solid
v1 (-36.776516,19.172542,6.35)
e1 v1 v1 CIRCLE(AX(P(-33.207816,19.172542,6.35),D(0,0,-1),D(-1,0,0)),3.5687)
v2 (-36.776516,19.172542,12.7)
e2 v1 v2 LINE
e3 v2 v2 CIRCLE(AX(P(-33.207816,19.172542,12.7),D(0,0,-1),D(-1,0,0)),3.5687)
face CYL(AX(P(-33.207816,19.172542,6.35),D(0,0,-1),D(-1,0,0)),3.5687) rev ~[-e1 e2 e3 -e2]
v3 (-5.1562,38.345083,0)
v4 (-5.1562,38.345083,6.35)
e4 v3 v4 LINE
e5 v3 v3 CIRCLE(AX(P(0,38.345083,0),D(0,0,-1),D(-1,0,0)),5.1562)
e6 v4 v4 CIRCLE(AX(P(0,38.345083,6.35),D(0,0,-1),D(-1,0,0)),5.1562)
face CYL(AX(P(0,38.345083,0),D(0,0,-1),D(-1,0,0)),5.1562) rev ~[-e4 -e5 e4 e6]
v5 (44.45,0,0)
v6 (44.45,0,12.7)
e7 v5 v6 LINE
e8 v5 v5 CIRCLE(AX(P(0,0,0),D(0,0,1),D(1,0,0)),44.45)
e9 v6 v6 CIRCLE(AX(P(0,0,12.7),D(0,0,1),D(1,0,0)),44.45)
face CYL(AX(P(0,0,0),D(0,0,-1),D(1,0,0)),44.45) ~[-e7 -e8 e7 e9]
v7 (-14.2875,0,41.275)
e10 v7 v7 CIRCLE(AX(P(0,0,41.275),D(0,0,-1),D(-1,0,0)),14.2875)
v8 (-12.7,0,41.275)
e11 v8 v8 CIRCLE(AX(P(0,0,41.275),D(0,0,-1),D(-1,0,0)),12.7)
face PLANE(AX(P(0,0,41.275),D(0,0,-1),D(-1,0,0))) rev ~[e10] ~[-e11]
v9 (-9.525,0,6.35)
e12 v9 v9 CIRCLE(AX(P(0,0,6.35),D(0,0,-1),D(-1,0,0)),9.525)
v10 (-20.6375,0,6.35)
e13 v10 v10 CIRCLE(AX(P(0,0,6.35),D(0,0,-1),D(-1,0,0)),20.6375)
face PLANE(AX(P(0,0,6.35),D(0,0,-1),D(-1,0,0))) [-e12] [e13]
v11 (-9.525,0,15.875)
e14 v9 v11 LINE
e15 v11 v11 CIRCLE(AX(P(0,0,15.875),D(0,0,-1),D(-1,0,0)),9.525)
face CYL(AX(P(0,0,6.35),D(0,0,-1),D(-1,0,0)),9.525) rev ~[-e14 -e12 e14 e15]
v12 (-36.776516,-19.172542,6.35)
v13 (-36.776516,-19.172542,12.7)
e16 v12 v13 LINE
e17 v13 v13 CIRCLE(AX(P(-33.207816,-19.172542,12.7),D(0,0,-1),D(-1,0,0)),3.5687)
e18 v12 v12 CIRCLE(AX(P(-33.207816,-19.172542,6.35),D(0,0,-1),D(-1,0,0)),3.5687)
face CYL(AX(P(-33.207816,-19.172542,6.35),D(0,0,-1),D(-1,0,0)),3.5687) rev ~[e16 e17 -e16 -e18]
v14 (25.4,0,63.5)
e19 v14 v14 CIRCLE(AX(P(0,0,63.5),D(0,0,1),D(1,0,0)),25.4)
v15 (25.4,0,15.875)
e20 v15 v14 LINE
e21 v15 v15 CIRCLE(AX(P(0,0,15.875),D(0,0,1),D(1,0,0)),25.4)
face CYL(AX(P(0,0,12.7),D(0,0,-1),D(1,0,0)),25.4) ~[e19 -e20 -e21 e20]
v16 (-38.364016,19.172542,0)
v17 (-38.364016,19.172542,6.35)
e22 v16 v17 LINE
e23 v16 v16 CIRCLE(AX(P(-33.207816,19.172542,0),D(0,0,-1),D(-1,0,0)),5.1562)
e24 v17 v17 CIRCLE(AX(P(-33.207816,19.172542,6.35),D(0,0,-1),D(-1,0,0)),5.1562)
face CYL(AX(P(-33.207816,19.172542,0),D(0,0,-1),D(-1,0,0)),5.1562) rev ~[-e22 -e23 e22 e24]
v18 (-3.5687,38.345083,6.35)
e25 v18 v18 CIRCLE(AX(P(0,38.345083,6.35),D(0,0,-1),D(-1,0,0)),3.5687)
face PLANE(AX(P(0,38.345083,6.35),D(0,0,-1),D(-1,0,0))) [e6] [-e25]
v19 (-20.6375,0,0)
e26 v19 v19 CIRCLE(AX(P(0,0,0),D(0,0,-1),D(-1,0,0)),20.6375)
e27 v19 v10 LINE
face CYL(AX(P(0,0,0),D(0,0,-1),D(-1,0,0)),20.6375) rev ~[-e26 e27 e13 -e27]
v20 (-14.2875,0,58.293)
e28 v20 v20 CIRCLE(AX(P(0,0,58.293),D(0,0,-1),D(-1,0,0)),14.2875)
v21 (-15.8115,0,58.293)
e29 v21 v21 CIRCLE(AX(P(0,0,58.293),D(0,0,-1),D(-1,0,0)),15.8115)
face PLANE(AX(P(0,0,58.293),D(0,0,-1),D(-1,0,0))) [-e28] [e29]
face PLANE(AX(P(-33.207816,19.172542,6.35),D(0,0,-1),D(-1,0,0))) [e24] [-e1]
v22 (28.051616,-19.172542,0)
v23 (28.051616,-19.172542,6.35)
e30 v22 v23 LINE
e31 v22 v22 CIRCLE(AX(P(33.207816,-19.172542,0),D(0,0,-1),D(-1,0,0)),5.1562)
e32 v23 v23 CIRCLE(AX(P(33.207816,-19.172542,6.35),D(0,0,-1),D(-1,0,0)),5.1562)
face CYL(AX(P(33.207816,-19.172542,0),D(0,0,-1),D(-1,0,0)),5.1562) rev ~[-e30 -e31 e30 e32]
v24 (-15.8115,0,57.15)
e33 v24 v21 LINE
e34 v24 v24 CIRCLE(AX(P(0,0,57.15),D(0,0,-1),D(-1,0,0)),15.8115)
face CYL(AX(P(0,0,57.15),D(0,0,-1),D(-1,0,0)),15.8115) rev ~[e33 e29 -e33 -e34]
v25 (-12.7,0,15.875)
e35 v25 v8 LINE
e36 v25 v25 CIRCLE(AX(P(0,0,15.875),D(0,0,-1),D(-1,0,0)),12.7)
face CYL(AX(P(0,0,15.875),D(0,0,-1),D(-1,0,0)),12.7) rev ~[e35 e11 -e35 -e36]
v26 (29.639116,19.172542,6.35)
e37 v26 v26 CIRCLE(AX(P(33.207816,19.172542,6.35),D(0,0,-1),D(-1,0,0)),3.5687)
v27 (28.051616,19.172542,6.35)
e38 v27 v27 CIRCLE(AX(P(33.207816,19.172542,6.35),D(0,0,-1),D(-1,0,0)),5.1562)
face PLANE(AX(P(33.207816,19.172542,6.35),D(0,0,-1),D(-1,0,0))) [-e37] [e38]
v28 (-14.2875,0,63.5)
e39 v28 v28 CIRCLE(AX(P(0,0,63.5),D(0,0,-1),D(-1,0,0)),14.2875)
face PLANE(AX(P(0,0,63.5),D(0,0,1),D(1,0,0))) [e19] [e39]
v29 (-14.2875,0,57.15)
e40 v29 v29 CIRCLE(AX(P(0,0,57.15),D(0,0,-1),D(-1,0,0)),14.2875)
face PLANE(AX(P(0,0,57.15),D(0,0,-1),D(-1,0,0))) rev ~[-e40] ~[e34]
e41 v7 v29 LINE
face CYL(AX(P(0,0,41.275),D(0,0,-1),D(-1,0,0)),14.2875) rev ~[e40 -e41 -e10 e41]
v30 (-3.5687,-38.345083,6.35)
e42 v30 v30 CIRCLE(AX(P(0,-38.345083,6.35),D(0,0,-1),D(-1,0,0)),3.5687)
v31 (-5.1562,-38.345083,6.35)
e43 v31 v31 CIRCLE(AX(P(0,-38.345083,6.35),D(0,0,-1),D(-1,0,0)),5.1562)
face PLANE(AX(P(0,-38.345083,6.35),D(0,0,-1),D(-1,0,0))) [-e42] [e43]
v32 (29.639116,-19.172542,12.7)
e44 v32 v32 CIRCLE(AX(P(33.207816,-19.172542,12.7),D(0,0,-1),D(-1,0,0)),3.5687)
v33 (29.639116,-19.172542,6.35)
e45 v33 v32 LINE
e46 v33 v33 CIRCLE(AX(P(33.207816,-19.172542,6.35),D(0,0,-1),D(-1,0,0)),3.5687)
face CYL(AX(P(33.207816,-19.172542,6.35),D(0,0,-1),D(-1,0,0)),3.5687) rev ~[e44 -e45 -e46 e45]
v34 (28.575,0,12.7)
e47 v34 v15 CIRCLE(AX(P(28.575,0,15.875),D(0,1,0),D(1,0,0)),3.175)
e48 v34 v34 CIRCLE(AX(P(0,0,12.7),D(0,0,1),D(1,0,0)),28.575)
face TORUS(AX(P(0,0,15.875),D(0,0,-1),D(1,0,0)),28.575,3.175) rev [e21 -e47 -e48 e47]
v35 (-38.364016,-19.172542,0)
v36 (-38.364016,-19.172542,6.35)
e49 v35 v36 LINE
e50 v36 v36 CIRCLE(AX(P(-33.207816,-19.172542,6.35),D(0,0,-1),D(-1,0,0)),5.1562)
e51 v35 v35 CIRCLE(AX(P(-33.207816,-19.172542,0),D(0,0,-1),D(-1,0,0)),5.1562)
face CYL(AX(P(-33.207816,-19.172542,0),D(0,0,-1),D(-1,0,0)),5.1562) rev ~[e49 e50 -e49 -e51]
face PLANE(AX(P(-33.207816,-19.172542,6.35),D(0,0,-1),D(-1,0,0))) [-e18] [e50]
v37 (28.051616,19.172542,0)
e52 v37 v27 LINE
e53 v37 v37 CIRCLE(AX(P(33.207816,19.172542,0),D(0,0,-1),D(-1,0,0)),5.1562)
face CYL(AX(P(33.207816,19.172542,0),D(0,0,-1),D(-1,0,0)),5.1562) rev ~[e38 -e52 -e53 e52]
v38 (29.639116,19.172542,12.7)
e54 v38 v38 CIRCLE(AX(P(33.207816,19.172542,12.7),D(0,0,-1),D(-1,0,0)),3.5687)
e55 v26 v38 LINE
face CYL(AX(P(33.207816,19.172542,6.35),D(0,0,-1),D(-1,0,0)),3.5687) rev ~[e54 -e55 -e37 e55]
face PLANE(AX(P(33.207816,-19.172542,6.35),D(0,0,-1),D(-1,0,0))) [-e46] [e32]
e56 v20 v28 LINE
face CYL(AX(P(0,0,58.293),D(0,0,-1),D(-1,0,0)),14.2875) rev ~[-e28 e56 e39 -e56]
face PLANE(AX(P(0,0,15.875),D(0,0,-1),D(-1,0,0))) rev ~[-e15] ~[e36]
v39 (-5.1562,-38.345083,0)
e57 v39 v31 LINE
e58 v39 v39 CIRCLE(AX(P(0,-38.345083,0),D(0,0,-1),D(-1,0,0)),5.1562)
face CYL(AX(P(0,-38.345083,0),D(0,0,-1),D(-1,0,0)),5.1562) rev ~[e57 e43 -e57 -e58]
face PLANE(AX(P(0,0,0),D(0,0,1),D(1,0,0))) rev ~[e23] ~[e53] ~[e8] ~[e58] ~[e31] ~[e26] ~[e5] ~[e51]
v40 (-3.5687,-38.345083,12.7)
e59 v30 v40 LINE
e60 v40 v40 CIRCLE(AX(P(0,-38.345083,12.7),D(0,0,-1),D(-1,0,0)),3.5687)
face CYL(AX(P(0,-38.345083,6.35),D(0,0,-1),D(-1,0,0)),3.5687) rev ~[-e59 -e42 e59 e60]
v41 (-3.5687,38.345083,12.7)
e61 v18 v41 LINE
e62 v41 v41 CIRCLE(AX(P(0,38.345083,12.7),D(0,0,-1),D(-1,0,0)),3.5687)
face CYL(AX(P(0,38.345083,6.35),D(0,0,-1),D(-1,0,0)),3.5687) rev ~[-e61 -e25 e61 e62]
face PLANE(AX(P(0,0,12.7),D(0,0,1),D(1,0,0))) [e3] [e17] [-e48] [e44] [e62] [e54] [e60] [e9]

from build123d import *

# Parameters (mm, degrees)
FLANGE_SKETCH_R                   = 44.45
FLANGE_3_5_DEPTH                  = 12.7
HUB_BOSS_SKETCH_R                 = 25.4
HUB_BOSS_2_DEPTH                  = 50.8
REAR_RECESS_SKETCH_R              = 20.6375
REAR_RECESS_1_625_DEPTH           = 6.35
PILOT_BORE_SKETCH_R               = 9.525
PILOT_BORE_0_75_DEPTH             = 9.525
INNER_BORE_SKETCH_R               = 12.7
INNER_BORE_1_0_DEPTH              = 25.4
BEARING_BORE_SKETCH_R             = 14.2875
BEARING_BORE_1_125_DEPTH          = 15.875
RETAINING_GROOVE_SKETCH_R         = 15.8115
RETAINING_RING_GROOVE_1_245_DEPTH = 1.143
THROUGH_BORE_SKETCH_R             = 14.2875
THROUGH_BORE_1_125_DEPTH          = 86.730267986
BOLT_COUNTERBORE_SKETCH_R         = 5.1562
BOLT_COUNTERBORES_6X_0_406_DEPTH  = 6.35
BOLT_HOLE_SKETCH_R                = 3.5687
BOLT_HOLES_6X_0_281_DEPTH         = 85.957209818
HUB_ROOT_FILLET_R0_125_R          = 3.175


with BuildPart() as part:
    # Flange Sketch → Flange Ø3.5 (new body)
    with BuildSketch(Plane.XY):
        Circle(FLANGE_SKETCH_R)
    extrude(amount=FLANGE_3_5_DEPTH)

    # Hub Boss Sketch → Hub Boss Ø2 (add)
    with BuildSketch(Plane.XY.offset(12.7)):
        Circle(HUB_BOSS_SKETCH_R)
    extrude(amount=HUB_BOSS_2_DEPTH)

    # Rear Recess Sketch → Rear Recess Ø1.625 (cut)
    with BuildSketch(Plane(origin=(0, 0, 0), x_dir=(-1, 0, 0), z_dir=(0, 0, -1))):
        Circle(REAR_RECESS_SKETCH_R)
    extrude(amount=-REAR_RECESS_1_625_DEPTH, mode=Mode.SUBTRACT)

    # Pilot Bore Sketch → Pilot Bore Ø0.75 (cut)
    with BuildSketch(Plane(origin=(0, 0, 6.35), x_dir=(-1, 0, 0), z_dir=(0, 0, -1))):
        Circle(PILOT_BORE_SKETCH_R)
    extrude(amount=-PILOT_BORE_0_75_DEPTH, mode=Mode.SUBTRACT)

    # Inner Bore Sketch → Inner Bore Ø1.0 (cut)
    with BuildSketch(Plane(origin=(0, 0, 15.875), x_dir=(-1, 0, 0), z_dir=(0, 0, -1))):
        Circle(INNER_BORE_SKETCH_R)
    extrude(amount=-INNER_BORE_1_0_DEPTH, mode=Mode.SUBTRACT)

    # Bearing Bore Sketch → Bearing Bore Ø1.125 (cut)
    with BuildSketch(Plane(origin=(0, 0, 41.275), x_dir=(-1, 0, 0), z_dir=(0, 0, -1))):
        Circle(BEARING_BORE_SKETCH_R)
    extrude(amount=-BEARING_BORE_1_125_DEPTH, mode=Mode.SUBTRACT)

    # Retaining Groove Sketch → Retaining Ring Groove Ø1.245 (cut)
    with BuildSketch(Plane(origin=(0, 0, 57.15), x_dir=(-1, 0, 0), z_dir=(0, 0, -1))):
        Circle(RETAINING_GROOVE_SKETCH_R)
    extrude(amount=-RETAINING_RING_GROOVE_1_245_DEPTH, mode=Mode.SUBTRACT)

    # Through Bore Sketch → Through Bore Ø1.125 (cut, through all)
    with BuildSketch(Plane(origin=(0, 0, 58.293), x_dir=(-1, 0, 0), z_dir=(0, 0, -1))):
        Circle(THROUGH_BORE_SKETCH_R)
    extrude(amount=-THROUGH_BORE_1_125_DEPTH, mode=Mode.SUBTRACT)

    # Bolt Counterbore Sketch → Bolt Counterbores 6xØ0.406 (cut)
    with BuildSketch(Plane(origin=(0, 0, 0), x_dir=(-1, 0, 0), z_dir=(0, 0, -1))):
        with Locations((0, 38.345083234)):
            Circle(BOLT_COUNTERBORE_SKETCH_R)
        with Locations((33.207816191, 19.172541617)):
            Circle(BOLT_COUNTERBORE_SKETCH_R)
        with Locations((33.207816191, -19.172541617)):
            Circle(BOLT_COUNTERBORE_SKETCH_R)
        with Locations((0, -38.345083234)):
            Circle(BOLT_COUNTERBORE_SKETCH_R)
        with Locations((-33.207816191, -19.172541617)):
            Circle(BOLT_COUNTERBORE_SKETCH_R)
        with Locations((-33.207816191, 19.172541617)):
            Circle(BOLT_COUNTERBORE_SKETCH_R)
    extrude(amount=-BOLT_COUNTERBORES_6X_0_406_DEPTH, mode=Mode.SUBTRACT)

    # Bolt Hole Sketch → Bolt Holes 6xØ0.281 (cut, through all)
    with BuildSketch(Plane(origin=(0, 0, 6.35), x_dir=(-1, 0, 0), z_dir=(0, 0, -1))):
        with Locations((0, 38.345083234)):
            Circle(BOLT_HOLE_SKETCH_R)
        with Locations((33.207816191, 19.172541617)):
            Circle(BOLT_HOLE_SKETCH_R)
        with Locations((33.207816191, -19.172541617)):
            Circle(BOLT_HOLE_SKETCH_R)
        with Locations((0, -38.345083234)):
            Circle(BOLT_HOLE_SKETCH_R)
        with Locations((-33.207816191, -19.172541617)):
            Circle(BOLT_HOLE_SKETCH_R)
        with Locations((-33.207816191, 19.172541617)):
            Circle(BOLT_HOLE_SKETCH_R)
    extrude(amount=-BOLT_HOLES_6X_0_281_DEPTH, mode=Mode.SUBTRACT)

    # Hub Root Fillet R0.125
    hub_root_fillet_r0_125_edges = [part.edges().sort_by_distance(p)[0] for p in [
        (-25.4, 0, 12.7),
    ]]
    fillet(hub_root_fillet_r0_125_edges, radius=HUB_ROOT_FILLET_R0_125_R)


solid = part.part
